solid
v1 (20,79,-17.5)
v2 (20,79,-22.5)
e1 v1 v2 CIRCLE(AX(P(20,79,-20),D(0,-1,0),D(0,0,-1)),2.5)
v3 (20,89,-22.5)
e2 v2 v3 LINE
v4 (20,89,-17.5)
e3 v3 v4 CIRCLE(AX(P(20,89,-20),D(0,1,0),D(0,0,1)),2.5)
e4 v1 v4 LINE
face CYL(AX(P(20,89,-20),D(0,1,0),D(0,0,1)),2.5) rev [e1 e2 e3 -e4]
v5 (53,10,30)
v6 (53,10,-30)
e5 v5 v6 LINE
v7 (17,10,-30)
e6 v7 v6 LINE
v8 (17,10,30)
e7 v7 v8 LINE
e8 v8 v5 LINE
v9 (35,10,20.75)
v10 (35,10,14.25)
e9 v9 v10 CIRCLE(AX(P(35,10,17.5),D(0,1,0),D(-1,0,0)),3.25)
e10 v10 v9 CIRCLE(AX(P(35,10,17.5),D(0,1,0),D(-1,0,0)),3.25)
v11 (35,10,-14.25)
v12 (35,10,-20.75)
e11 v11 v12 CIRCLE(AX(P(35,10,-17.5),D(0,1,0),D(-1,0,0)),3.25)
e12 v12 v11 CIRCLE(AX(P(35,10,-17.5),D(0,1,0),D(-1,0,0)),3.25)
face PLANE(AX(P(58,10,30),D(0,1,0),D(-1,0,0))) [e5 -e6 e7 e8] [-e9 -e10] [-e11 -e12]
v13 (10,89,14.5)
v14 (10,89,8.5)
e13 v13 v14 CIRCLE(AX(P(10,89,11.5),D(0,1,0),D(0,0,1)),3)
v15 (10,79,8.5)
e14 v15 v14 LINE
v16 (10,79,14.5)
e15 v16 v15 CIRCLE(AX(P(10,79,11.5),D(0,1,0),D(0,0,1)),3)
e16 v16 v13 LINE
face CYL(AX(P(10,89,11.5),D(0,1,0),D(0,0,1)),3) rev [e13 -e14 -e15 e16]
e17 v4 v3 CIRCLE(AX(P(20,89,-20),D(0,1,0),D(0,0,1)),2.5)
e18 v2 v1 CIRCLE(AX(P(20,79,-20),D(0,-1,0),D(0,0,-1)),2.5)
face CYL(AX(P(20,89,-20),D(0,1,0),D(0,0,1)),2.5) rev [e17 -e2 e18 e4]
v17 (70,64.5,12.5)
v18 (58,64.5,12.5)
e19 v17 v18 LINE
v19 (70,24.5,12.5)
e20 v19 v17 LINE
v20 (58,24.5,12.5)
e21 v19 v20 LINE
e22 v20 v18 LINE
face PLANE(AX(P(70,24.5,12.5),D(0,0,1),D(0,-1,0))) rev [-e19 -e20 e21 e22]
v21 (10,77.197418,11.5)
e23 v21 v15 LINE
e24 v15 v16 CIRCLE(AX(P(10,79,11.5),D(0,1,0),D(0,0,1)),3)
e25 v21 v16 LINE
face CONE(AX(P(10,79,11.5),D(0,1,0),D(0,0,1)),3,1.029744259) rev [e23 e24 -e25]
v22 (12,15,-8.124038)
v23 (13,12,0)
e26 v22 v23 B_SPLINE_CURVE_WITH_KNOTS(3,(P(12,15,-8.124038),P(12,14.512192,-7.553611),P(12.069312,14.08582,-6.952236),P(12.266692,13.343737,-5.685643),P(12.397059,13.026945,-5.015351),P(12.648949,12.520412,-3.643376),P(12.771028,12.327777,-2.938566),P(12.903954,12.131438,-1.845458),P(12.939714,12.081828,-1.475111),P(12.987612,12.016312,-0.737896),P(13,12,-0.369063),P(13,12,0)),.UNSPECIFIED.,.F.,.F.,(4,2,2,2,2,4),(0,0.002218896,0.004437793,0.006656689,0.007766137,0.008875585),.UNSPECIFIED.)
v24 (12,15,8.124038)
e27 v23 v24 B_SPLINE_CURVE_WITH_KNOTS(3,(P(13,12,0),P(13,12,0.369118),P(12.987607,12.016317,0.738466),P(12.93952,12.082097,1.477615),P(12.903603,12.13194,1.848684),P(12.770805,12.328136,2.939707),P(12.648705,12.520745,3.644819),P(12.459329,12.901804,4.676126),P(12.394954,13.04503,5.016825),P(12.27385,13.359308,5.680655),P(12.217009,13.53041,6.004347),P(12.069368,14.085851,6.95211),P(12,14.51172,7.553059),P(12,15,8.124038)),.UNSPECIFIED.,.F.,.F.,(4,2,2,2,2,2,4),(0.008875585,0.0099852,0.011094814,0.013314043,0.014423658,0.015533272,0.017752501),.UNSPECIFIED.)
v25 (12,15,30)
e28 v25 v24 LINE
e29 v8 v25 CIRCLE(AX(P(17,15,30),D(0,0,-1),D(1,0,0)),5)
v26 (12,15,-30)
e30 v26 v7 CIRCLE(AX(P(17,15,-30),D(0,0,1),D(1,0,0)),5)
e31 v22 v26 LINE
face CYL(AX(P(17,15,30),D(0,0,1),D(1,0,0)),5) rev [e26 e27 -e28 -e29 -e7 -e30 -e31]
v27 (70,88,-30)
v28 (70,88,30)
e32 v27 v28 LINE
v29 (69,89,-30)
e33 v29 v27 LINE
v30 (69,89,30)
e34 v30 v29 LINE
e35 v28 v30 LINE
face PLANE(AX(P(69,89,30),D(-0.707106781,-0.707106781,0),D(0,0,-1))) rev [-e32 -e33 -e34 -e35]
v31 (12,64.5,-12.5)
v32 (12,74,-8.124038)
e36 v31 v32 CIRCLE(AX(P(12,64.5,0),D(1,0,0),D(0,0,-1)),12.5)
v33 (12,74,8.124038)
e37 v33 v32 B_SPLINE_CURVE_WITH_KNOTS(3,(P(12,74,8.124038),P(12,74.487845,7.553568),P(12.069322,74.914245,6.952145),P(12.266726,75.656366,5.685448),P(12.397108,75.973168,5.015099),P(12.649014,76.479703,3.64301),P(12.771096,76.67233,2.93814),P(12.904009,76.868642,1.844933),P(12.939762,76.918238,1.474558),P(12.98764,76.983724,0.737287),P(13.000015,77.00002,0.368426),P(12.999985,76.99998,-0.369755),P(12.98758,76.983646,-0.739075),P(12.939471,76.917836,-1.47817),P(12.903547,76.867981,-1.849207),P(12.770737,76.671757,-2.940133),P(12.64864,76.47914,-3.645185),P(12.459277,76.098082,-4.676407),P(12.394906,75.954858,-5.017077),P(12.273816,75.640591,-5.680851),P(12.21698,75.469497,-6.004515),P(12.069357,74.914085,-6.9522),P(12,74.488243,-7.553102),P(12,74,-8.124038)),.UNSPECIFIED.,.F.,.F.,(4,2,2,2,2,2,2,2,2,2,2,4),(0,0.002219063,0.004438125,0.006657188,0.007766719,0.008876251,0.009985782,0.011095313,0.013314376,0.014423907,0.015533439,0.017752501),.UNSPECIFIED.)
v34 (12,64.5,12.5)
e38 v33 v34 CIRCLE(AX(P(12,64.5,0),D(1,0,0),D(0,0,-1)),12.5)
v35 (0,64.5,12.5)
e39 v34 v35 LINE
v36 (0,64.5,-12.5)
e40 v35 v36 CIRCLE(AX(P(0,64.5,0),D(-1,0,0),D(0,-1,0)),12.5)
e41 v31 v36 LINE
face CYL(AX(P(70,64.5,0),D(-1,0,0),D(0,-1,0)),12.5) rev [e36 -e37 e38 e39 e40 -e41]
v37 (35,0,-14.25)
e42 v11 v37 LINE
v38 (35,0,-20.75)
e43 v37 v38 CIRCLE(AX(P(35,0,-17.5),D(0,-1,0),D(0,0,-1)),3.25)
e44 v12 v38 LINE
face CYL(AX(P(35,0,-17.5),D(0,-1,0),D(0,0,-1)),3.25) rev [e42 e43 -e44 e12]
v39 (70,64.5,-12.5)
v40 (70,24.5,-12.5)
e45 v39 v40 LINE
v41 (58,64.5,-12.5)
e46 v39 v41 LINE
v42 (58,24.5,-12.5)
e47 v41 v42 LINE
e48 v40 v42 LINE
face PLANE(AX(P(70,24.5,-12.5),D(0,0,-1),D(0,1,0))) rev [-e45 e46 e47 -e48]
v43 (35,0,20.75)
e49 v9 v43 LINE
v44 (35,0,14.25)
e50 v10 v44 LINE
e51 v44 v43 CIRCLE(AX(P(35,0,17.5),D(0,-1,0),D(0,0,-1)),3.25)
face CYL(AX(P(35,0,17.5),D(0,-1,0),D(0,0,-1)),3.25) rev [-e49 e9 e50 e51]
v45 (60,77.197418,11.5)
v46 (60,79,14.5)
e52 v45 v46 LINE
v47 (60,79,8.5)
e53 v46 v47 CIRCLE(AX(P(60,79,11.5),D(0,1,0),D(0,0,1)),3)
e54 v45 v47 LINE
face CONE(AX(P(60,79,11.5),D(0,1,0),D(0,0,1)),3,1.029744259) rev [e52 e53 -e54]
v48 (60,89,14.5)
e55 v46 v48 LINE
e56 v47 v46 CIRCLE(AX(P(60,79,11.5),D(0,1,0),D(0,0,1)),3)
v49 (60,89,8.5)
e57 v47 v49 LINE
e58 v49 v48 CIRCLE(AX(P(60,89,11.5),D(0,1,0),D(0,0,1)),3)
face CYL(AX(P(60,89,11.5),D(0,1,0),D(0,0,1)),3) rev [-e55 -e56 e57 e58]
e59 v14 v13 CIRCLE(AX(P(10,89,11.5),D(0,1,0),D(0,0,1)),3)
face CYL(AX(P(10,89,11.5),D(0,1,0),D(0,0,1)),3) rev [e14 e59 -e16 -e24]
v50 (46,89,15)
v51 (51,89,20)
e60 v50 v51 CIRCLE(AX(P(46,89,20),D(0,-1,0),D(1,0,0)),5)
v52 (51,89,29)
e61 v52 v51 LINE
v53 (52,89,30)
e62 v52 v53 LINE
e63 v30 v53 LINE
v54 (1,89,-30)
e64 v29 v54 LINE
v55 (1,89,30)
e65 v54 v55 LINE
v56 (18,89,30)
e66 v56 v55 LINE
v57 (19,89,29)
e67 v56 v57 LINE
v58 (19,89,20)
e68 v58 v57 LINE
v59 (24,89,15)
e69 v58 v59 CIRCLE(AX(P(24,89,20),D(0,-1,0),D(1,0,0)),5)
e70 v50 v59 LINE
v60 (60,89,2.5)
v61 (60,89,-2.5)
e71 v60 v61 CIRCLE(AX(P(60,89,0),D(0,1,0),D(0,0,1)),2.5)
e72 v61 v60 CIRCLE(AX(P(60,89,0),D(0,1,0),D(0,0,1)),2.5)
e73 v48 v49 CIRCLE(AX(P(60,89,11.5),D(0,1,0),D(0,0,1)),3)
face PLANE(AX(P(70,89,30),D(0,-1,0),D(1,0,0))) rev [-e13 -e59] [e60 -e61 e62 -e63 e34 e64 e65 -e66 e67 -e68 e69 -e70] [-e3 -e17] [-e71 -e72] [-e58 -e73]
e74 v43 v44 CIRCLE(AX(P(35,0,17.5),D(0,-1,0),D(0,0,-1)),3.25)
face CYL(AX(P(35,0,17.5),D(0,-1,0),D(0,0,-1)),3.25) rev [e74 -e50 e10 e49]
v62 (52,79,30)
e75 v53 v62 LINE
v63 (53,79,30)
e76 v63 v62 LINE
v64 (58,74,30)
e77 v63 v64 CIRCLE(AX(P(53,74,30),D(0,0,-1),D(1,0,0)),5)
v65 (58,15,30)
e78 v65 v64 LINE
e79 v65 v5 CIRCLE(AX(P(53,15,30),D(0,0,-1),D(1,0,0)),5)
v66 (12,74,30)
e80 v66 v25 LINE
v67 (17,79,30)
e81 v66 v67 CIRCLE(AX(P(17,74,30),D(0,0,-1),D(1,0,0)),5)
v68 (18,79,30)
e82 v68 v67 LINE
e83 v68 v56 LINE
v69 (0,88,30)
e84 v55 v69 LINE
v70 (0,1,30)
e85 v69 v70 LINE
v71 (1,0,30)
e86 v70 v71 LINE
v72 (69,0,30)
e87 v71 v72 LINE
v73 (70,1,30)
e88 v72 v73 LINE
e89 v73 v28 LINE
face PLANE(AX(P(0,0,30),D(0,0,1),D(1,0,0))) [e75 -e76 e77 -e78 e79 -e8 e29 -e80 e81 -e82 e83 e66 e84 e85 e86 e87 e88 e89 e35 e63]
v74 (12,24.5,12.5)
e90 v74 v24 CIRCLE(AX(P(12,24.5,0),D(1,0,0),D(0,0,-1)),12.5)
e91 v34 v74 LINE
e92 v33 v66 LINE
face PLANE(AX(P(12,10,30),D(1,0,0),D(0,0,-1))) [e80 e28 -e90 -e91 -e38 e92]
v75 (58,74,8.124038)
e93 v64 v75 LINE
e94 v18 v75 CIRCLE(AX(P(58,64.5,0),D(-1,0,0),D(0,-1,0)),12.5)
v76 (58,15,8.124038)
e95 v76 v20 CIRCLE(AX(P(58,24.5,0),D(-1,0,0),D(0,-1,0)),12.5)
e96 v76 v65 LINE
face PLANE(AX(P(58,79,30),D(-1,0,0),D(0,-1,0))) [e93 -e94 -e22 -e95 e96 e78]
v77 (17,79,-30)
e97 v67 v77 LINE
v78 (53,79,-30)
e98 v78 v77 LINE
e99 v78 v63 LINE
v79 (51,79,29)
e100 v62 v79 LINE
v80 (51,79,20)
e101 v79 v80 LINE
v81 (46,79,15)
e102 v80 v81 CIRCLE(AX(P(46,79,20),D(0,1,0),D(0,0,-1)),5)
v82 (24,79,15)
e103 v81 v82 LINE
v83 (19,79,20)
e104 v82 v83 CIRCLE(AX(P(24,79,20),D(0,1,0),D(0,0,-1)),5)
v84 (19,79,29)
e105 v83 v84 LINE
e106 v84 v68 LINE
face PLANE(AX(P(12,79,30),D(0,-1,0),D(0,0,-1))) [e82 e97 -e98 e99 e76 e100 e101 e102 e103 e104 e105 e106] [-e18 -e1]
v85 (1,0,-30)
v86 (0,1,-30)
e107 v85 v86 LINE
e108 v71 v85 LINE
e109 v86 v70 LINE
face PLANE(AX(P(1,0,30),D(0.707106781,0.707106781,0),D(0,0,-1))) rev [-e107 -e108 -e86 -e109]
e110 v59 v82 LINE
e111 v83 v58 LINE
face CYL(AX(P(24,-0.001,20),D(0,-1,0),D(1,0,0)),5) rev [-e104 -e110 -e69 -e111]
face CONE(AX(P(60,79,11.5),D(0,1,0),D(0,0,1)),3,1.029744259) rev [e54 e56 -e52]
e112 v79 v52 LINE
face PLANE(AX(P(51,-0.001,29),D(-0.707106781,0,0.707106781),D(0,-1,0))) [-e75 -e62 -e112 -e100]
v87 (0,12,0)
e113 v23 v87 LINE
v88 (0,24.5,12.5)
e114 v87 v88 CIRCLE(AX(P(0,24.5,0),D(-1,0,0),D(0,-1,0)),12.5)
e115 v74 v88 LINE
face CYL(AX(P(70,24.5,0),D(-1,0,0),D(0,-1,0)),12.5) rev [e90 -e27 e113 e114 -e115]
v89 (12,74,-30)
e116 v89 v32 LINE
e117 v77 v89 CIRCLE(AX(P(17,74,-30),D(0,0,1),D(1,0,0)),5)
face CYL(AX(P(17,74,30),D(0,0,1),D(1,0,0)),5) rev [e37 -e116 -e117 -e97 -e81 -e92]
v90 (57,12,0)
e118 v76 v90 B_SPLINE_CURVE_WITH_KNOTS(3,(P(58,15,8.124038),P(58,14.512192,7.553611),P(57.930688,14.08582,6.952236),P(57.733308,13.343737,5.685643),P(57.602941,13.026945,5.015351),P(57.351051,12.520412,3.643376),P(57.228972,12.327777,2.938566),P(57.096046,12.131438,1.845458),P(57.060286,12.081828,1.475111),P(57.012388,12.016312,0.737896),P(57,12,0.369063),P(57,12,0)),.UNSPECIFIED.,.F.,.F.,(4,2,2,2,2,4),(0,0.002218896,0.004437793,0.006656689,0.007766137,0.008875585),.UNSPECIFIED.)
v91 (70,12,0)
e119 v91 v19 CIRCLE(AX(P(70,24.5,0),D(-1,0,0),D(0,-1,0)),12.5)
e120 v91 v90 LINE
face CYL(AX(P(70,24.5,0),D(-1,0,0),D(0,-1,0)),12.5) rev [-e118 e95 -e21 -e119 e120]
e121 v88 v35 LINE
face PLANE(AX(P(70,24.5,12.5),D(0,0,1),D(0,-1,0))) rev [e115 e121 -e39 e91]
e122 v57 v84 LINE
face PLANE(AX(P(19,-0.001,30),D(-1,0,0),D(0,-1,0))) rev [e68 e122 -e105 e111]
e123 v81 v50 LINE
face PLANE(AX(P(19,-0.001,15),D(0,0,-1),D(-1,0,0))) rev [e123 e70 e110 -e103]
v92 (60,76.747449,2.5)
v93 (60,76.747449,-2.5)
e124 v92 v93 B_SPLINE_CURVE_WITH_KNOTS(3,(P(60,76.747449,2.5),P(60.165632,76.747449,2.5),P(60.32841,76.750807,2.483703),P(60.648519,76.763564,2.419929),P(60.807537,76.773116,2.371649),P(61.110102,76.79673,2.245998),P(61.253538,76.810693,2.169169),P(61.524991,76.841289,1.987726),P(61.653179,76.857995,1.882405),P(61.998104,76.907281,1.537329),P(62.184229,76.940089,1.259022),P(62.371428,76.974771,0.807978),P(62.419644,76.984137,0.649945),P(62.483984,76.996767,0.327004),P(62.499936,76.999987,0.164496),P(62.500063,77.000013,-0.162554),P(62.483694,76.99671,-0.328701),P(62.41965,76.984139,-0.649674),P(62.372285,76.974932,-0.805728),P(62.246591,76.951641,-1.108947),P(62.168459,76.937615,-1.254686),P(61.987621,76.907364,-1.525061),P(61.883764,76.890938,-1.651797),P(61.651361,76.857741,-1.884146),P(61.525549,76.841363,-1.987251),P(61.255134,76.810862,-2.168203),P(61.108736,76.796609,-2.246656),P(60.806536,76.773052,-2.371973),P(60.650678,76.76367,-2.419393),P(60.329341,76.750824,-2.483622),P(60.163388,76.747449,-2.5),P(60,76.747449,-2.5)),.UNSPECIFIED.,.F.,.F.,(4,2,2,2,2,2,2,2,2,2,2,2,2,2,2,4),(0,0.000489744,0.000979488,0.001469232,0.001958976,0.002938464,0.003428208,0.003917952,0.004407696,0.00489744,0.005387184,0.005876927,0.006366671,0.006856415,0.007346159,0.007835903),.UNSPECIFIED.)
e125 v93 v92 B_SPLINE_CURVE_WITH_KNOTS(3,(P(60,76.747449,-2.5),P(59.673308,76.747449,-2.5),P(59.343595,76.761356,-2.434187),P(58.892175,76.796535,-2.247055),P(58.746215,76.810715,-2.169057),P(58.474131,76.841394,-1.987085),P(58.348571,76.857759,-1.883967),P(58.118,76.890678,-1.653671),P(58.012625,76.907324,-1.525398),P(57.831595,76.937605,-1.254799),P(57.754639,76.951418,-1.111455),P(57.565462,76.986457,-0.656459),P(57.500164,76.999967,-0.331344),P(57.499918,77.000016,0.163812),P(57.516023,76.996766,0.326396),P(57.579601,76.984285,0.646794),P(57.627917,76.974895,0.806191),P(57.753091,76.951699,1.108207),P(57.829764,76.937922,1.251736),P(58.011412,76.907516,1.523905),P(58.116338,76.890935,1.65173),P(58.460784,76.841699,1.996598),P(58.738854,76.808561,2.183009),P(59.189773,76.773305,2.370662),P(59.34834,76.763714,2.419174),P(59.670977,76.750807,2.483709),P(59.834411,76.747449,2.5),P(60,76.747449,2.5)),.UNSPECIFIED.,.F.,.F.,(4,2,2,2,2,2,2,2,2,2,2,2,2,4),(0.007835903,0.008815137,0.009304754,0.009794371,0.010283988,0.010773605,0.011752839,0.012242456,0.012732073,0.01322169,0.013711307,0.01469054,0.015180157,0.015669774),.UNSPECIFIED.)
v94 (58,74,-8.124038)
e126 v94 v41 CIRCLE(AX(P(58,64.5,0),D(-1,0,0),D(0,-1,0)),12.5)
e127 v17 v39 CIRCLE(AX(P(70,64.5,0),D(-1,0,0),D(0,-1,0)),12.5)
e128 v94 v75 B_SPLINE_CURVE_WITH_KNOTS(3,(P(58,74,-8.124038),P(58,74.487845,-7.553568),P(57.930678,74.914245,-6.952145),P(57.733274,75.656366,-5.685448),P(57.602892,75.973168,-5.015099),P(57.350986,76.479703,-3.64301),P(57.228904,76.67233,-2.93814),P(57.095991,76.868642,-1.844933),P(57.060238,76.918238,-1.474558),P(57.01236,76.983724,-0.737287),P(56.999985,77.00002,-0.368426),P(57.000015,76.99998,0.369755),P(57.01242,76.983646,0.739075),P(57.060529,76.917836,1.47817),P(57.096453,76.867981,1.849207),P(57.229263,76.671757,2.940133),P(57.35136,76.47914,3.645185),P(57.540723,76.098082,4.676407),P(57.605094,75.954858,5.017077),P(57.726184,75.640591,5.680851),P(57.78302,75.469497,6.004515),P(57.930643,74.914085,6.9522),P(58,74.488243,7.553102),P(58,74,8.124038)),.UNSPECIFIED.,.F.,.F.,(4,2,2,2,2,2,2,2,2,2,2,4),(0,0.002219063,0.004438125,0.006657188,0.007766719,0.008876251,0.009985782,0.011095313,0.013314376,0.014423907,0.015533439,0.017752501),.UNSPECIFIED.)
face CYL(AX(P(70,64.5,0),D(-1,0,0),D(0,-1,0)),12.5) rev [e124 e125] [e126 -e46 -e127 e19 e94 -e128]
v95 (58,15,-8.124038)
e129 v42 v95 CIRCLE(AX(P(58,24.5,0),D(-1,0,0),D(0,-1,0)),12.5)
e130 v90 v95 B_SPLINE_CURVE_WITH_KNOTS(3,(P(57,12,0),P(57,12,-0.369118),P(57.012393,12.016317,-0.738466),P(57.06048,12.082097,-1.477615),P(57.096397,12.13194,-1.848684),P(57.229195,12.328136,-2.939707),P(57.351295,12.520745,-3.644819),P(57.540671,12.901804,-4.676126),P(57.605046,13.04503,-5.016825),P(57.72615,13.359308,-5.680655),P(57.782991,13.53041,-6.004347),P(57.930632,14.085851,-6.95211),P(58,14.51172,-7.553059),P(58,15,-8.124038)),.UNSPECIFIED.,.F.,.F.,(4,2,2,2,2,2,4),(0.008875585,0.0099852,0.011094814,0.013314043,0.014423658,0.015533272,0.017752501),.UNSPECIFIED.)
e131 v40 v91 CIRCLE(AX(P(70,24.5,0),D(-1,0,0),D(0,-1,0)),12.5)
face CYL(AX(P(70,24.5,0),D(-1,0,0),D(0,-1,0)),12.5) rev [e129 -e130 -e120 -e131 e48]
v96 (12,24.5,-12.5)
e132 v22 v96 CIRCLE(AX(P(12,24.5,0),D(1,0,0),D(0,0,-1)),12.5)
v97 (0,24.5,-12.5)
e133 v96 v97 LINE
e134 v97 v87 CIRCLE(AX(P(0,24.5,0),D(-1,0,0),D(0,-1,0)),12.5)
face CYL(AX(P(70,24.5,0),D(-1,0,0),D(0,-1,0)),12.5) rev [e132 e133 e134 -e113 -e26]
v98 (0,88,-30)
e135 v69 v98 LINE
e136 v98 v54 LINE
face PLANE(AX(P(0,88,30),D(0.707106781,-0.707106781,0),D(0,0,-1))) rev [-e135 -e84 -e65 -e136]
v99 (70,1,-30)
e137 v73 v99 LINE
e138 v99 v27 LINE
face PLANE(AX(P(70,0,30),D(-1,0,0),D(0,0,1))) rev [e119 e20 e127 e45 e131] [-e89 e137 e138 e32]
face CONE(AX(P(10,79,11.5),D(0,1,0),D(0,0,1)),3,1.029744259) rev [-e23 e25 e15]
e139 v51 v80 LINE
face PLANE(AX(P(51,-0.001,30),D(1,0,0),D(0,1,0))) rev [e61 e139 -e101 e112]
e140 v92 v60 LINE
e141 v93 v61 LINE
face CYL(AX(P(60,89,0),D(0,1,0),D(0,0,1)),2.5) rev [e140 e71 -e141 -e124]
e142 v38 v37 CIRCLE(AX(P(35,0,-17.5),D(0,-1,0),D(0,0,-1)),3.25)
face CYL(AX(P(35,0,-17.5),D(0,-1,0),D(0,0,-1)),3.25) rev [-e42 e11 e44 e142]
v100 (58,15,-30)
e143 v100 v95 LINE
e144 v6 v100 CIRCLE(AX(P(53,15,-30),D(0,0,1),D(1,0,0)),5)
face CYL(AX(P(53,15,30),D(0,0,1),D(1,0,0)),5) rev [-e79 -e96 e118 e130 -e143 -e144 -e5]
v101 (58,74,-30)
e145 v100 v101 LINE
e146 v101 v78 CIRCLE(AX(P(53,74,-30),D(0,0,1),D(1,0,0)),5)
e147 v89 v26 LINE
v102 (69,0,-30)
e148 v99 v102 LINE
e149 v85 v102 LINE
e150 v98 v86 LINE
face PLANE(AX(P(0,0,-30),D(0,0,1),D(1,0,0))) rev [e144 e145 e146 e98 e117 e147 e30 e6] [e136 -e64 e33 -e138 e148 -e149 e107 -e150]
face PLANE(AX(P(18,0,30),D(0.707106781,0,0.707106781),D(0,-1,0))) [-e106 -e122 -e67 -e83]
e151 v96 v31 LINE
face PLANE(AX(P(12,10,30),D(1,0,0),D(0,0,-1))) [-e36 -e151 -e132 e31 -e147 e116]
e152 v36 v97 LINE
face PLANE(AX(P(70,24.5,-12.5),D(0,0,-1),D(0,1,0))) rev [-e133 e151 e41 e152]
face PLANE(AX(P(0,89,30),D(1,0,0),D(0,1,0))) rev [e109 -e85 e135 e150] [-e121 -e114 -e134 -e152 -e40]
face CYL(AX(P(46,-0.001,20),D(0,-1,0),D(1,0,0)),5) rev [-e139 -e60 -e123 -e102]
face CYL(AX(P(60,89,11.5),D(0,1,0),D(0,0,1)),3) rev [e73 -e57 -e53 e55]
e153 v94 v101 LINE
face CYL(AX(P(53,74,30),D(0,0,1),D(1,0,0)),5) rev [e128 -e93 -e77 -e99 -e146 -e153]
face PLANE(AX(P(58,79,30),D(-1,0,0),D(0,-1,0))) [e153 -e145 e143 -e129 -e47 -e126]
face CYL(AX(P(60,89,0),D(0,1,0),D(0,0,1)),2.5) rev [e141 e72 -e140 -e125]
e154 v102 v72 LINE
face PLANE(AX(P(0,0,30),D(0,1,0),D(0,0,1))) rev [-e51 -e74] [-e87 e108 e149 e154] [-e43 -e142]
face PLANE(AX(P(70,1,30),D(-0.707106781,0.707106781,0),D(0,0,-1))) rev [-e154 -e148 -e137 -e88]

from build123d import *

# Parameters (mm, degrees)
SKETCH1_W                      = 70
SKETCH1_H                      = 89
SKETCH1_W_2                    = 46
SKETCH1_H_2                    = 69
BOSS_EXTRUDE1_DEPTH            = 30
FILLET2_R                      = 5
CUT_EXTRUDE1_DEPTH             = 118.136672311
M6_TAPPED_HOLE1_D              = 5
M6_TAPPED_HOLE1_DEPTH          = 15
M6_TAPPED_HOLE1_TIP            = 1.502151548
F_6_0_6_DIAMETER_HOLE1_D       = 6
F_6_0_6_DIAMETER_HOLE1_DEPTH   = 10
F_6_0_6_DIAMETER_HOLE1_TIP     = 1.802581857
F_6_5_6_5_DIAMETER_HOLE2_D     = 6.5
F_6_5_6_5_DIAMETER_HOLE2_DEPTH = 12
F_6_5_6_5_DIAMETER_HOLE2_TIP   = 1.952797012
CUT_EXTRUDE2_REACH             = 119.137
SKETCH10_W                     = 32
SKETCH10_H                     = 15
FILLET1_R                      = 5
CHAMFER1_SIZE                  = 1


with BuildPart() as part:
    # Sketch1 → Boss-Extrude1 (new, symmetric)
    with BuildSketch(Plane.XY):
        with Locations((35, 44.5)):
            Rectangle(SKETCH1_W, SKETCH1_H)
        with Locations((35, 44.5)):
            Rectangle(SKETCH1_W_2, SKETCH1_H_2, mode=Mode.SUBTRACT)
    extrude(amount=BOSS_EXTRUDE1_DEPTH, both=True)

    # Fillet2
    fillet2_edges = [part.edges().sort_by_distance(p)[0] for p in [
        (58, 10, 0),
        (58, 79, 0),
        (12, 79, 0),
        (12, 10, 0),
    ]]
    fillet(fillet2_edges, radius=FILLET2_R)

    # Sketch2 → Cut-Extrude1 (cut, through all)
    with BuildSketch(Plane.ZY):
        with BuildLine():
            Line((-12.5, 24.5), (-12.5, 64.5))
            ThreePointArc((-12.5, 64.5), (0, 77), (12.5, 64.5))
            Line((12.5, 64.5), (12.5, 24.5))
            ThreePointArc((12.5, 24.5), (0, 12), (-12.5, 24.5))
        make_face()
    extrude(amount=-CUT_EXTRUDE1_DEPTH, mode=Mode.SUBTRACT)

    # M6 Tapped Hole1
    with Locations(Plane(origin=(0, 89, 0), x_dir=(1, 0, 0), z_dir=(0, 1, 0))):
        with Locations((60, 0), (20, 20)):
            Hole(M6_TAPPED_HOLE1_D / 2, depth=M6_TAPPED_HOLE1_DEPTH)
            with Locations((0, 0, -(M6_TAPPED_HOLE1_DEPTH + M6_TAPPED_HOLE1_TIP / 2))):  # 118° drill point
                Cone(0, M6_TAPPED_HOLE1_D / 2, M6_TAPPED_HOLE1_TIP, mode=Mode.SUBTRACT)

    # Ø6.0 (6) Diameter Hole1
    with Locations(Plane(origin=(0, 89, 0), x_dir=(1, 0, 0), z_dir=(0, 1, 0))):
        with Locations((10, -11.5), (60, -11.5)):
            Hole(F_6_0_6_DIAMETER_HOLE1_D / 2, depth=F_6_0_6_DIAMETER_HOLE1_DEPTH)
            with Locations((0, 0, -(F_6_0_6_DIAMETER_HOLE1_DEPTH + F_6_0_6_DIAMETER_HOLE1_TIP / 2))):  # 118° drill point
                Cone(0, F_6_0_6_DIAMETER_HOLE1_D / 2, F_6_0_6_DIAMETER_HOLE1_TIP, mode=Mode.SUBTRACT)

    # Ø6.5 (6.5) Diameter Hole2
    with Locations(Plane(origin=(0, 0, 0), x_dir=(-1, 0, 0), z_dir=(0, -1, 0))):
        with Locations((-35, -17.5), (-35, 17.5)):
            Hole(F_6_5_6_5_DIAMETER_HOLE2_D / 2, depth=F_6_5_6_5_DIAMETER_HOLE2_DEPTH)
            with Locations((0, 0, -(F_6_5_6_5_DIAMETER_HOLE2_DEPTH + F_6_5_6_5_DIAMETER_HOLE2_TIP / 2))):  # 118° drill point
                Cone(0, F_6_5_6_5_DIAMETER_HOLE2_D / 2, F_6_5_6_5_DIAMETER_HOLE2_TIP, mode=Mode.SUBTRACT)

    # Sketch10 → Cut-Extrude2 (cut, up to next)
    with BuildSketch(Plane(origin=(0, 89, 0), x_dir=(1, 0, 0), z_dir=(0, 1, 0)), mode=Mode.PRIVATE) as cut_extrude2_sk1:
        with Locations((35, -22.5)):
            Rectangle(SKETCH10_W, SKETCH10_H)
    cut_extrude2_tool1 = extrude(cut_extrude2_sk1.sketch, amount=-CUT_EXTRUDE2_REACH, mode=Mode.PRIVATE) & part.part
    add(cut_extrude2_tool1.solids().sort_by_distance((35, 89, 22.5))[0], mode=Mode.SUBTRACT)

    # Fillet1
    fillet1_edges = [part.edges().sort_by_distance(p)[0] for p in [
        (51, 84, 15),
        (19, 84, 15),
    ]]
    fillet(fillet1_edges, radius=FILLET1_R)

    # Chamfer1
    chamfer1_edges = [part.edges().sort_by_distance(p)[0] for p in [
        (19, 84, 30),
        (51, 84, 30),
        (0, 89, 0),
        (70, 89, 0),
        (70, 0, 0),
        (0, 0, 0),
    ]]
    chamfer(chamfer1_edges, length=CHAMFER1_SIZE)


solid = part.part
